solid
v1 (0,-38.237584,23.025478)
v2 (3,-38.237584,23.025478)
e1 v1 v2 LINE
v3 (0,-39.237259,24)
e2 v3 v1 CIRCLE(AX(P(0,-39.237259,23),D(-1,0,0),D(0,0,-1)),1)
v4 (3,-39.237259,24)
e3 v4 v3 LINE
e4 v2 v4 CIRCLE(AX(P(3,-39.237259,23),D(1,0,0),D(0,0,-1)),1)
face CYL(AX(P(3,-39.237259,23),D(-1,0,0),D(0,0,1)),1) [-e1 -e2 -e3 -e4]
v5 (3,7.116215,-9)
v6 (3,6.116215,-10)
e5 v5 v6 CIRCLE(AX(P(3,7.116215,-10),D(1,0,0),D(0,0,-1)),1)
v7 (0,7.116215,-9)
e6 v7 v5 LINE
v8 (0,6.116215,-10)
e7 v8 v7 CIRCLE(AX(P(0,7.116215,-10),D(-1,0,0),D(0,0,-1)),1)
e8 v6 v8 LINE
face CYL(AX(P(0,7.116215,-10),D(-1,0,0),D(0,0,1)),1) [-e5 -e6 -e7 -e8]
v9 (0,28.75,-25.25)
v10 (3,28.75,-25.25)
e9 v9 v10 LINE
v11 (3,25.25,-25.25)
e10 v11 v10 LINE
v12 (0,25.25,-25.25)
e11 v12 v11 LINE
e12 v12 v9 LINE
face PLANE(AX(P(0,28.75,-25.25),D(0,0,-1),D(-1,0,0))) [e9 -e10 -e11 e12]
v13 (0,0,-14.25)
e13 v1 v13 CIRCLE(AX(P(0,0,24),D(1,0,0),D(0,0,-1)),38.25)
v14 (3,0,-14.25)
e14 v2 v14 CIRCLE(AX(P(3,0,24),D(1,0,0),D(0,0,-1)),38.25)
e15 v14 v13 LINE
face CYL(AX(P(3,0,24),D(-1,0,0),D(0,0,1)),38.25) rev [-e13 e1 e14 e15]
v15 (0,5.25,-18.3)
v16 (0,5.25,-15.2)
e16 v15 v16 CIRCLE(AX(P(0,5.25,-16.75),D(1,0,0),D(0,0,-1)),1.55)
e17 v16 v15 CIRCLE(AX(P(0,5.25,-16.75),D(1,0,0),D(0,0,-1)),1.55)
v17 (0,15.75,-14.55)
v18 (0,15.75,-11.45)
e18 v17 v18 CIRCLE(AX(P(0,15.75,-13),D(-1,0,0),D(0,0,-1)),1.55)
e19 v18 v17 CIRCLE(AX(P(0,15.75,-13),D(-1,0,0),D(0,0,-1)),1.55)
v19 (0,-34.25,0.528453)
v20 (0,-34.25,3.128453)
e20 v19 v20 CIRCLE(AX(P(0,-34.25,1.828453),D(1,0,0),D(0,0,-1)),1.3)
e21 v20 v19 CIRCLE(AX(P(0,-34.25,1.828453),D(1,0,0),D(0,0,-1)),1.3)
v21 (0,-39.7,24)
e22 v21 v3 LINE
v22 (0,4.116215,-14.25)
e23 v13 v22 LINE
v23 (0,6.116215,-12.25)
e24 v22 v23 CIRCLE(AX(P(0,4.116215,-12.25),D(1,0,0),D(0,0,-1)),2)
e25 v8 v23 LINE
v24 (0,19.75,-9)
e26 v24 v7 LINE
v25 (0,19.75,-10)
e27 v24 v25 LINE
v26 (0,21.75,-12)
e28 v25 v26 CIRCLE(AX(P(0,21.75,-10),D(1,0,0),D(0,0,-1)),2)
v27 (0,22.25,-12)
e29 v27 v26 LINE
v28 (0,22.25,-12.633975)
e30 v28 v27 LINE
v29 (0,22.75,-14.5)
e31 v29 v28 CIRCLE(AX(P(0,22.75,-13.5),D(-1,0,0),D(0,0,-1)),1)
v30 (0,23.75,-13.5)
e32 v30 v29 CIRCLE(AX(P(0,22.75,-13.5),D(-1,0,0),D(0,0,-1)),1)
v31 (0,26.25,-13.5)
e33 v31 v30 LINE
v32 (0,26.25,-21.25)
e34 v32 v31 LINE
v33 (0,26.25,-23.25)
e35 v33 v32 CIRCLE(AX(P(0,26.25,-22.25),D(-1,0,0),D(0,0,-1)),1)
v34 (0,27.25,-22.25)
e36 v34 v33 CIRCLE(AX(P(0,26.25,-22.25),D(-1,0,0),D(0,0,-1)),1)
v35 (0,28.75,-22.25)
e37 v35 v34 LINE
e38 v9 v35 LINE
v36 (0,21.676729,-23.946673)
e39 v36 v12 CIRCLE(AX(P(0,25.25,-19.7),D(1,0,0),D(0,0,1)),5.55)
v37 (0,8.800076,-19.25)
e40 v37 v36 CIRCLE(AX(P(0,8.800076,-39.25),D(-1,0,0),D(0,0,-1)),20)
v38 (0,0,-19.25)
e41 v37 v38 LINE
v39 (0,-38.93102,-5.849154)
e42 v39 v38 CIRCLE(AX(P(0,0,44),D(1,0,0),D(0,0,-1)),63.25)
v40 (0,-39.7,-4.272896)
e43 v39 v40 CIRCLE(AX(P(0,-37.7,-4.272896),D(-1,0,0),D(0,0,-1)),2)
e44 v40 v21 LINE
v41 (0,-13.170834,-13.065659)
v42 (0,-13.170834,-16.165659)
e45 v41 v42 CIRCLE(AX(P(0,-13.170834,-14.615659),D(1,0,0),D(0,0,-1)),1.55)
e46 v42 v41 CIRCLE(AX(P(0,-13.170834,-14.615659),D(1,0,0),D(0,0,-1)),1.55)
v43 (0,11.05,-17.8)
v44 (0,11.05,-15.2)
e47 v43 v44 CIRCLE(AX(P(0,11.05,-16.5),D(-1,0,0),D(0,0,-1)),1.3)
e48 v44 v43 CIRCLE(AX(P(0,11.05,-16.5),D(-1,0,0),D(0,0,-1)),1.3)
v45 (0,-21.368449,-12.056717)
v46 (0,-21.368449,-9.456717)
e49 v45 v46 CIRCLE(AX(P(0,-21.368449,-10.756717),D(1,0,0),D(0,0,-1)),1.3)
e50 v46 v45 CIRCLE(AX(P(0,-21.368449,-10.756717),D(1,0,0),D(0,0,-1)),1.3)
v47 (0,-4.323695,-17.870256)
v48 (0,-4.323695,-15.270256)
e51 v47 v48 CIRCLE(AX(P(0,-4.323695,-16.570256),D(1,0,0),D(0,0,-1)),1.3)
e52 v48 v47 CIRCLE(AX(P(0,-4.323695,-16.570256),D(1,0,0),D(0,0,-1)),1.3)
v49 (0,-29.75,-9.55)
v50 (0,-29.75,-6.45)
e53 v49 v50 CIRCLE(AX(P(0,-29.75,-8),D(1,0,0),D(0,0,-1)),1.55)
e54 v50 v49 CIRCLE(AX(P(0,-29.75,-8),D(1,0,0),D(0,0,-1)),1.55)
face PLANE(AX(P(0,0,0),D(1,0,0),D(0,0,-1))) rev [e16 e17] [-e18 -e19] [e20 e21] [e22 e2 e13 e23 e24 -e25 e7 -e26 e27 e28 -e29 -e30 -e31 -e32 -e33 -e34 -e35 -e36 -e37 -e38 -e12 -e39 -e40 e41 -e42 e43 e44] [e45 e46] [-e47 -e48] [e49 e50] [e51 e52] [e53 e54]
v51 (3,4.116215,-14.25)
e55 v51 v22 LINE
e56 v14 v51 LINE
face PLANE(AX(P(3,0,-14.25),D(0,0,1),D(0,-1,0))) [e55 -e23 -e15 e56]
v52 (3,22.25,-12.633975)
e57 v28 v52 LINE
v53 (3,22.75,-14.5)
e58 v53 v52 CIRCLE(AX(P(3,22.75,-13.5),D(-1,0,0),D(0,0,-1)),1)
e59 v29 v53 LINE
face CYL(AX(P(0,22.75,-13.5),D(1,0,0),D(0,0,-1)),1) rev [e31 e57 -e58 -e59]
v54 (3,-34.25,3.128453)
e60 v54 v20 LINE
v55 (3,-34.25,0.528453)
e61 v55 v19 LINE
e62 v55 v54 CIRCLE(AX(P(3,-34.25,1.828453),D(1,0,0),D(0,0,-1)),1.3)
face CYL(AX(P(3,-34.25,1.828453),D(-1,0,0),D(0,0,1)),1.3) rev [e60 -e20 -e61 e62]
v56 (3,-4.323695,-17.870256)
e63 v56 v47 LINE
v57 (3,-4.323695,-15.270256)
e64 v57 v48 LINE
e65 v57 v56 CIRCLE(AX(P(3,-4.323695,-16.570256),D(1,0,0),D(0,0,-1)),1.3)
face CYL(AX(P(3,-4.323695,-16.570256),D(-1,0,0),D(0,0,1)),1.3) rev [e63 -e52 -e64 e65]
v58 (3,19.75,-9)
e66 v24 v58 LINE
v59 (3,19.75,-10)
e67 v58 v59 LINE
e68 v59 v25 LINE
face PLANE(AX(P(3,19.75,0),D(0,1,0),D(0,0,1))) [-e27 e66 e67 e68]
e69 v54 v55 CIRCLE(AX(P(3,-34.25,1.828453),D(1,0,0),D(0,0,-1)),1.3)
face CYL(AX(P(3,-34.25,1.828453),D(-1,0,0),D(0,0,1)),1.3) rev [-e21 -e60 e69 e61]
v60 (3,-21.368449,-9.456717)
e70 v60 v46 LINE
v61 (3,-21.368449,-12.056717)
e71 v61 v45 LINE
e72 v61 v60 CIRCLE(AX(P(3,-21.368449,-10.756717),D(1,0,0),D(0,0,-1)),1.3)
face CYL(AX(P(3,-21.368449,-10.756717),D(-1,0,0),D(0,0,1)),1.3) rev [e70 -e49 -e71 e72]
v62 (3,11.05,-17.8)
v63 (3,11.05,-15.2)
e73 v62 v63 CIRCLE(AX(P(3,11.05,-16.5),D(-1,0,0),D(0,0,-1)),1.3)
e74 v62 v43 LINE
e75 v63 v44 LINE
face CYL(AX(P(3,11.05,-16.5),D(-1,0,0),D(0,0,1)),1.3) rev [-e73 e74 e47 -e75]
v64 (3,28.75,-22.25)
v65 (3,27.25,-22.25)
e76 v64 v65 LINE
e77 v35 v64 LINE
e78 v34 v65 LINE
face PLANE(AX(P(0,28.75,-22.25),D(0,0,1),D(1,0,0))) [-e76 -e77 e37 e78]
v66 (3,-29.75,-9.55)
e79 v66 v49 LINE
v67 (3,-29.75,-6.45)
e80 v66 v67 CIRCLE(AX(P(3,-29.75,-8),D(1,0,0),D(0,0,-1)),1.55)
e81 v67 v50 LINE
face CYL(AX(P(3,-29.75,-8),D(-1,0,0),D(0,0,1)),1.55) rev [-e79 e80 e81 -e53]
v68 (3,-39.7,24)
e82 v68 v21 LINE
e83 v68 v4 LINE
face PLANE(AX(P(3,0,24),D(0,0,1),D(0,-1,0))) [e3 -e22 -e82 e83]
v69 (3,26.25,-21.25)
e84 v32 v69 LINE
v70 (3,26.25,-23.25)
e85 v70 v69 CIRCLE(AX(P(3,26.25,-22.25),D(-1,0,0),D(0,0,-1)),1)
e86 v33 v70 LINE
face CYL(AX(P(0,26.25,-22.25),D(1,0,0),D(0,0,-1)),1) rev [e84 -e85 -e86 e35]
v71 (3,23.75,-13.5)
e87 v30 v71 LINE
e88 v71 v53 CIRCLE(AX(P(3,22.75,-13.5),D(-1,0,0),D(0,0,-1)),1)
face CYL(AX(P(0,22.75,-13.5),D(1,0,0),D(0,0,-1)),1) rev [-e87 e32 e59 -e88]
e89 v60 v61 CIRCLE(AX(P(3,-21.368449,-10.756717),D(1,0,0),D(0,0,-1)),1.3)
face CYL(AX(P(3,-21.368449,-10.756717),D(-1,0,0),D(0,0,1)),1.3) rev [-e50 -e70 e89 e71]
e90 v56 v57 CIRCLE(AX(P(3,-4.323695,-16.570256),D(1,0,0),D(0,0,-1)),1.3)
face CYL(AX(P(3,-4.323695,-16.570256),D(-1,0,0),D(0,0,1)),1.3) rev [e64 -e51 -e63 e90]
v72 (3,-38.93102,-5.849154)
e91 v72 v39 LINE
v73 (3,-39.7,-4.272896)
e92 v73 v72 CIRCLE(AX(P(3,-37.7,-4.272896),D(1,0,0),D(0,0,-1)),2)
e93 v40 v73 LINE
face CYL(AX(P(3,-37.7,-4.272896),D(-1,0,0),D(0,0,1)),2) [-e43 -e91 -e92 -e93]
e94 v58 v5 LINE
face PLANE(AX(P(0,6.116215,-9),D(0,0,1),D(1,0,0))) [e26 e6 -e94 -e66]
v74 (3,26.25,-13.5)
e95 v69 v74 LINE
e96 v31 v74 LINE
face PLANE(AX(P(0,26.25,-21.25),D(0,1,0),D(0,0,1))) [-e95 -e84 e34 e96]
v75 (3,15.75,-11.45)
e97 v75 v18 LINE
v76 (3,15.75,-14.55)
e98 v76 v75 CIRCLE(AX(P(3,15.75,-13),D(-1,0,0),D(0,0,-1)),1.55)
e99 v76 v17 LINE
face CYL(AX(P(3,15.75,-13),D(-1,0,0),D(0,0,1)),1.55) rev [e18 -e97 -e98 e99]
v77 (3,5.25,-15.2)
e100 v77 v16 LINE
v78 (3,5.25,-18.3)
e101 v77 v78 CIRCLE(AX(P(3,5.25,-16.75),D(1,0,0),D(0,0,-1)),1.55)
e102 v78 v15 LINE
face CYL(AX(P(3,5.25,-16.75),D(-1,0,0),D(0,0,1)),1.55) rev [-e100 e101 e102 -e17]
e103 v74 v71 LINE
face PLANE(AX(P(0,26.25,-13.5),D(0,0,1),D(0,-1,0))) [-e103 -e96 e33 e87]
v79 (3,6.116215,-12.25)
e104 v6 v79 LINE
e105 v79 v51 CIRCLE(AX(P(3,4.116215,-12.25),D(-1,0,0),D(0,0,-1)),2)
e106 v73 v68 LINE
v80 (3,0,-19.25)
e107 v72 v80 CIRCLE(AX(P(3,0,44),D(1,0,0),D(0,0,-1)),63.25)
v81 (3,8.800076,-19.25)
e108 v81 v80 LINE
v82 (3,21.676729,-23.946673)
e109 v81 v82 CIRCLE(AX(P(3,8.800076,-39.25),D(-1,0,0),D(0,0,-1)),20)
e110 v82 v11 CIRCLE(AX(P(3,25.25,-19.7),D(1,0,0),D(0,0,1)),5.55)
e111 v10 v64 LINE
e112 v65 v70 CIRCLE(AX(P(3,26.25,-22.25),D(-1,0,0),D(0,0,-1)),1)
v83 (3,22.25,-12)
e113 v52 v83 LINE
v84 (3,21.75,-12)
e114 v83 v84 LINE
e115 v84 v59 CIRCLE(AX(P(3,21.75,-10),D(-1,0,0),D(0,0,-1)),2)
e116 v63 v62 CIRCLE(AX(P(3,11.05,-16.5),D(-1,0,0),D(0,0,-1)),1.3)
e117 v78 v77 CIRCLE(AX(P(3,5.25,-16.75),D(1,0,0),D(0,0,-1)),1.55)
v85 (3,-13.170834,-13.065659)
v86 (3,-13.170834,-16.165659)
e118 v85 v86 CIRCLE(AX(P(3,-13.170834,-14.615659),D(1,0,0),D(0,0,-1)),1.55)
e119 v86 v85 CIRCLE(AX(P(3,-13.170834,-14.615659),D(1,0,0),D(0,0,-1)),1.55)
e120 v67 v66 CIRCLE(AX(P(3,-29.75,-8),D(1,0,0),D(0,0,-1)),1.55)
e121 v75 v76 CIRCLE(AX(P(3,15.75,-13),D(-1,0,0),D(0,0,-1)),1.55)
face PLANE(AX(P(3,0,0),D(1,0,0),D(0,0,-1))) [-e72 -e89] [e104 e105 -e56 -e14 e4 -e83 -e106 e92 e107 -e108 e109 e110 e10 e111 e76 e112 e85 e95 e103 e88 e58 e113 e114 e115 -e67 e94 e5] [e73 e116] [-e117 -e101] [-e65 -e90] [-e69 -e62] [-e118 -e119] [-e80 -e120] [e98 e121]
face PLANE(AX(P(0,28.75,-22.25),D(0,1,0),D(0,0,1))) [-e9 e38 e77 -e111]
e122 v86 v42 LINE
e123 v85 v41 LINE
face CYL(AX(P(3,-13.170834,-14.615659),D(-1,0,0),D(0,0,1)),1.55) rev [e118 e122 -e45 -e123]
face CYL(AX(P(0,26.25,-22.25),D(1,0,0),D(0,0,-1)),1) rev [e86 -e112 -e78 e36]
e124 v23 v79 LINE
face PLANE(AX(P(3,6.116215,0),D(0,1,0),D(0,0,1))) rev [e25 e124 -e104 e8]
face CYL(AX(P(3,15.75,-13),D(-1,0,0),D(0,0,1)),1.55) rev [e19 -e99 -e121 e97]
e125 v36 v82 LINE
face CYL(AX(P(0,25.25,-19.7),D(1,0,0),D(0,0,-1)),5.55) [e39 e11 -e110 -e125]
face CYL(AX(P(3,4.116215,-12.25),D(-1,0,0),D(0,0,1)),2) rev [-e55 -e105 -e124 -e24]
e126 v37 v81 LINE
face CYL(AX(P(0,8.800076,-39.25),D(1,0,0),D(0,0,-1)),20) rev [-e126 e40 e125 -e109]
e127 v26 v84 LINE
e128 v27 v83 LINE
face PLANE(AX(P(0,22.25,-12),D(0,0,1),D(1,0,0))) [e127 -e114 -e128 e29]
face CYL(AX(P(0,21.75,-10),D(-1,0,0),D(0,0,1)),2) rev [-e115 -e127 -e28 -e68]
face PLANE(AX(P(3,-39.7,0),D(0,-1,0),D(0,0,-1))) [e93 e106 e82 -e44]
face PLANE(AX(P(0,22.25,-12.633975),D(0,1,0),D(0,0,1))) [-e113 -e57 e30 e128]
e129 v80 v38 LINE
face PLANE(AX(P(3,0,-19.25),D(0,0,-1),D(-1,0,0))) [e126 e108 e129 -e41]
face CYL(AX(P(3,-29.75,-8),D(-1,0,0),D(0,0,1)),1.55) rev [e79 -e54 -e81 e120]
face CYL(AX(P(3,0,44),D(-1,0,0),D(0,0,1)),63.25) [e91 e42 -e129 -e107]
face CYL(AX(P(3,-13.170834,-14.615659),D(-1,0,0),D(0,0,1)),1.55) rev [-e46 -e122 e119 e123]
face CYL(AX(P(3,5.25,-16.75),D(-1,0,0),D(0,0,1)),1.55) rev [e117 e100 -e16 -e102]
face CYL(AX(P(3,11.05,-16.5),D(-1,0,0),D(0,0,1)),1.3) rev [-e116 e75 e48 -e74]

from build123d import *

# Parameters (mm, degrees)
SKETCH_1_R      = 1.55
SKETCH_1_R_2    = 1.3
EXTRUDE_1_DEPTH = 3
SKETCH_2_W      = 0.25
SKETCH_2_H      = 13.633784975
EXTRUDE_2_DEPTH = 3
FILLET_R2_1_R   = 2
FILLET_R1_2_R   = 1


with BuildPart() as part:
    # 草图1 → 凸台-拉伸1 (new body)
    with BuildSketch(Plane(origin=(0, 0, 0), x_dir=(0, 0, -1), z_dir=(1, 0, 0))):
        with BuildLine():
            Line((9.25, 19.75), (9.25, 6.116215025))
            Line((9.25, 6.116215025), (14.25, 6.116215025))
            Line((14.25, 6.116215025), (14.25, 0))
            ThreePointArc((14.25, 0), (3.04683438, -27.04683438), (-24, -38.25))
            Line((-24, -38.25), (-24, -39.7))
            Line((-24, -39.7), (5.238932767, -39.7))
            ThreePointArc((5.238932767, -39.7), (15.644467461, -21.049940647), (19.25, 0))
            Line((19.25, 0), (19.25, 19.75))
            Line((19.25, 19.75), (9.25, 19.75))
        make_face()
        with Locations((13, 15.75)):
            Circle(SKETCH_1_R, mode=Mode.SUBTRACT)
        with Locations((16.75, 5.25)):
            Circle(SKETCH_1_R, mode=Mode.SUBTRACT)
        with Locations((16.5, 11.05)):
            Circle(SKETCH_1_R_2, mode=Mode.SUBTRACT)
        with Locations((-1.828452918, -34.25)):
            Circle(SKETCH_1_R_2, mode=Mode.SUBTRACT)
        with Locations((8, -29.75)):
            Circle(SKETCH_1_R, mode=Mode.SUBTRACT)
        with Locations((10.756717193, -21.368448937)):
            Circle(SKETCH_1_R_2, mode=Mode.SUBTRACT)
        with Locations((14.615659071, -13.170834237)):
            Circle(SKETCH_1_R, mode=Mode.SUBTRACT)
        with Locations((16.57025586, -4.32369512)):
            Circle(SKETCH_1_R_2, mode=Mode.SUBTRACT)
    extrude(amount=EXTRUDE_1_DEPTH)

    # 草图2 → 凸台-拉伸2 (add, through all)
    with BuildSketch(Plane(origin=(3, 0, 0), x_dir=(0, 0, -1), z_dir=(1, 0, 0))):
        with Locations((9.125, 12.933107513)):
            Rectangle(SKETCH_2_W, SKETCH_2_H)
        with BuildLine():
            Line((12, 19.75), (19.25, 19.75))
            Line((19.25, 19.75), (19.25, 8.800075988))
            ThreePointArc((19.25, 8.800075988), (20.460820452, 15.653303833), (23.94667319, 21.676728835))
            ThreePointArc((23.94667319, 21.676728835), (24.913997325, 23.348229273), (25.25, 25.25))
            Line((25.25, 25.25), (25.25, 28.75))
            Line((25.25, 28.75), (22.25, 28.75))
            Line((22.25, 28.75), (22.25, 27.25))
            ThreePointArc((22.25, 27.25), (22.957106781, 25.542893219), (21.25, 26.25))
            Line((21.25, 26.25), (13.5, 26.25))
            Line((13.5, 26.25), (13.5, 23.75))
            ThreePointArc((13.5, 23.75), (14.366025404, 22.25), (12.633974596, 22.25))
            Line((12.633974596, 22.25), (12, 22.25))
            Line((12, 22.25), (12, 19.75))
        make_face()
    extrude(amount=-EXTRUDE_2_DEPTH)

    # R2 圆角1
    fillet_r2_1_edges = [part.edges().sort_by_distance(p)[0] for p in [
        (1.5, -39.7, -5.238932767),
        (1.5, 6.116215025, -14.25),
        (1.5, 19.75, -12),
    ]]
    fillet(fillet_r2_1_edges, radius=FILLET_R2_1_R)

    # R1 圆角2
    fillet_r1_2_edges = [part.edges().sort_by_distance(p)[0] for p in [
        (1.5, -38.25, 24),
        (1.5, 6.116215025, -9),
    ]]
    fillet(fillet_r1_2_edges, radius=FILLET_R1_2_R)


solid = part.part
